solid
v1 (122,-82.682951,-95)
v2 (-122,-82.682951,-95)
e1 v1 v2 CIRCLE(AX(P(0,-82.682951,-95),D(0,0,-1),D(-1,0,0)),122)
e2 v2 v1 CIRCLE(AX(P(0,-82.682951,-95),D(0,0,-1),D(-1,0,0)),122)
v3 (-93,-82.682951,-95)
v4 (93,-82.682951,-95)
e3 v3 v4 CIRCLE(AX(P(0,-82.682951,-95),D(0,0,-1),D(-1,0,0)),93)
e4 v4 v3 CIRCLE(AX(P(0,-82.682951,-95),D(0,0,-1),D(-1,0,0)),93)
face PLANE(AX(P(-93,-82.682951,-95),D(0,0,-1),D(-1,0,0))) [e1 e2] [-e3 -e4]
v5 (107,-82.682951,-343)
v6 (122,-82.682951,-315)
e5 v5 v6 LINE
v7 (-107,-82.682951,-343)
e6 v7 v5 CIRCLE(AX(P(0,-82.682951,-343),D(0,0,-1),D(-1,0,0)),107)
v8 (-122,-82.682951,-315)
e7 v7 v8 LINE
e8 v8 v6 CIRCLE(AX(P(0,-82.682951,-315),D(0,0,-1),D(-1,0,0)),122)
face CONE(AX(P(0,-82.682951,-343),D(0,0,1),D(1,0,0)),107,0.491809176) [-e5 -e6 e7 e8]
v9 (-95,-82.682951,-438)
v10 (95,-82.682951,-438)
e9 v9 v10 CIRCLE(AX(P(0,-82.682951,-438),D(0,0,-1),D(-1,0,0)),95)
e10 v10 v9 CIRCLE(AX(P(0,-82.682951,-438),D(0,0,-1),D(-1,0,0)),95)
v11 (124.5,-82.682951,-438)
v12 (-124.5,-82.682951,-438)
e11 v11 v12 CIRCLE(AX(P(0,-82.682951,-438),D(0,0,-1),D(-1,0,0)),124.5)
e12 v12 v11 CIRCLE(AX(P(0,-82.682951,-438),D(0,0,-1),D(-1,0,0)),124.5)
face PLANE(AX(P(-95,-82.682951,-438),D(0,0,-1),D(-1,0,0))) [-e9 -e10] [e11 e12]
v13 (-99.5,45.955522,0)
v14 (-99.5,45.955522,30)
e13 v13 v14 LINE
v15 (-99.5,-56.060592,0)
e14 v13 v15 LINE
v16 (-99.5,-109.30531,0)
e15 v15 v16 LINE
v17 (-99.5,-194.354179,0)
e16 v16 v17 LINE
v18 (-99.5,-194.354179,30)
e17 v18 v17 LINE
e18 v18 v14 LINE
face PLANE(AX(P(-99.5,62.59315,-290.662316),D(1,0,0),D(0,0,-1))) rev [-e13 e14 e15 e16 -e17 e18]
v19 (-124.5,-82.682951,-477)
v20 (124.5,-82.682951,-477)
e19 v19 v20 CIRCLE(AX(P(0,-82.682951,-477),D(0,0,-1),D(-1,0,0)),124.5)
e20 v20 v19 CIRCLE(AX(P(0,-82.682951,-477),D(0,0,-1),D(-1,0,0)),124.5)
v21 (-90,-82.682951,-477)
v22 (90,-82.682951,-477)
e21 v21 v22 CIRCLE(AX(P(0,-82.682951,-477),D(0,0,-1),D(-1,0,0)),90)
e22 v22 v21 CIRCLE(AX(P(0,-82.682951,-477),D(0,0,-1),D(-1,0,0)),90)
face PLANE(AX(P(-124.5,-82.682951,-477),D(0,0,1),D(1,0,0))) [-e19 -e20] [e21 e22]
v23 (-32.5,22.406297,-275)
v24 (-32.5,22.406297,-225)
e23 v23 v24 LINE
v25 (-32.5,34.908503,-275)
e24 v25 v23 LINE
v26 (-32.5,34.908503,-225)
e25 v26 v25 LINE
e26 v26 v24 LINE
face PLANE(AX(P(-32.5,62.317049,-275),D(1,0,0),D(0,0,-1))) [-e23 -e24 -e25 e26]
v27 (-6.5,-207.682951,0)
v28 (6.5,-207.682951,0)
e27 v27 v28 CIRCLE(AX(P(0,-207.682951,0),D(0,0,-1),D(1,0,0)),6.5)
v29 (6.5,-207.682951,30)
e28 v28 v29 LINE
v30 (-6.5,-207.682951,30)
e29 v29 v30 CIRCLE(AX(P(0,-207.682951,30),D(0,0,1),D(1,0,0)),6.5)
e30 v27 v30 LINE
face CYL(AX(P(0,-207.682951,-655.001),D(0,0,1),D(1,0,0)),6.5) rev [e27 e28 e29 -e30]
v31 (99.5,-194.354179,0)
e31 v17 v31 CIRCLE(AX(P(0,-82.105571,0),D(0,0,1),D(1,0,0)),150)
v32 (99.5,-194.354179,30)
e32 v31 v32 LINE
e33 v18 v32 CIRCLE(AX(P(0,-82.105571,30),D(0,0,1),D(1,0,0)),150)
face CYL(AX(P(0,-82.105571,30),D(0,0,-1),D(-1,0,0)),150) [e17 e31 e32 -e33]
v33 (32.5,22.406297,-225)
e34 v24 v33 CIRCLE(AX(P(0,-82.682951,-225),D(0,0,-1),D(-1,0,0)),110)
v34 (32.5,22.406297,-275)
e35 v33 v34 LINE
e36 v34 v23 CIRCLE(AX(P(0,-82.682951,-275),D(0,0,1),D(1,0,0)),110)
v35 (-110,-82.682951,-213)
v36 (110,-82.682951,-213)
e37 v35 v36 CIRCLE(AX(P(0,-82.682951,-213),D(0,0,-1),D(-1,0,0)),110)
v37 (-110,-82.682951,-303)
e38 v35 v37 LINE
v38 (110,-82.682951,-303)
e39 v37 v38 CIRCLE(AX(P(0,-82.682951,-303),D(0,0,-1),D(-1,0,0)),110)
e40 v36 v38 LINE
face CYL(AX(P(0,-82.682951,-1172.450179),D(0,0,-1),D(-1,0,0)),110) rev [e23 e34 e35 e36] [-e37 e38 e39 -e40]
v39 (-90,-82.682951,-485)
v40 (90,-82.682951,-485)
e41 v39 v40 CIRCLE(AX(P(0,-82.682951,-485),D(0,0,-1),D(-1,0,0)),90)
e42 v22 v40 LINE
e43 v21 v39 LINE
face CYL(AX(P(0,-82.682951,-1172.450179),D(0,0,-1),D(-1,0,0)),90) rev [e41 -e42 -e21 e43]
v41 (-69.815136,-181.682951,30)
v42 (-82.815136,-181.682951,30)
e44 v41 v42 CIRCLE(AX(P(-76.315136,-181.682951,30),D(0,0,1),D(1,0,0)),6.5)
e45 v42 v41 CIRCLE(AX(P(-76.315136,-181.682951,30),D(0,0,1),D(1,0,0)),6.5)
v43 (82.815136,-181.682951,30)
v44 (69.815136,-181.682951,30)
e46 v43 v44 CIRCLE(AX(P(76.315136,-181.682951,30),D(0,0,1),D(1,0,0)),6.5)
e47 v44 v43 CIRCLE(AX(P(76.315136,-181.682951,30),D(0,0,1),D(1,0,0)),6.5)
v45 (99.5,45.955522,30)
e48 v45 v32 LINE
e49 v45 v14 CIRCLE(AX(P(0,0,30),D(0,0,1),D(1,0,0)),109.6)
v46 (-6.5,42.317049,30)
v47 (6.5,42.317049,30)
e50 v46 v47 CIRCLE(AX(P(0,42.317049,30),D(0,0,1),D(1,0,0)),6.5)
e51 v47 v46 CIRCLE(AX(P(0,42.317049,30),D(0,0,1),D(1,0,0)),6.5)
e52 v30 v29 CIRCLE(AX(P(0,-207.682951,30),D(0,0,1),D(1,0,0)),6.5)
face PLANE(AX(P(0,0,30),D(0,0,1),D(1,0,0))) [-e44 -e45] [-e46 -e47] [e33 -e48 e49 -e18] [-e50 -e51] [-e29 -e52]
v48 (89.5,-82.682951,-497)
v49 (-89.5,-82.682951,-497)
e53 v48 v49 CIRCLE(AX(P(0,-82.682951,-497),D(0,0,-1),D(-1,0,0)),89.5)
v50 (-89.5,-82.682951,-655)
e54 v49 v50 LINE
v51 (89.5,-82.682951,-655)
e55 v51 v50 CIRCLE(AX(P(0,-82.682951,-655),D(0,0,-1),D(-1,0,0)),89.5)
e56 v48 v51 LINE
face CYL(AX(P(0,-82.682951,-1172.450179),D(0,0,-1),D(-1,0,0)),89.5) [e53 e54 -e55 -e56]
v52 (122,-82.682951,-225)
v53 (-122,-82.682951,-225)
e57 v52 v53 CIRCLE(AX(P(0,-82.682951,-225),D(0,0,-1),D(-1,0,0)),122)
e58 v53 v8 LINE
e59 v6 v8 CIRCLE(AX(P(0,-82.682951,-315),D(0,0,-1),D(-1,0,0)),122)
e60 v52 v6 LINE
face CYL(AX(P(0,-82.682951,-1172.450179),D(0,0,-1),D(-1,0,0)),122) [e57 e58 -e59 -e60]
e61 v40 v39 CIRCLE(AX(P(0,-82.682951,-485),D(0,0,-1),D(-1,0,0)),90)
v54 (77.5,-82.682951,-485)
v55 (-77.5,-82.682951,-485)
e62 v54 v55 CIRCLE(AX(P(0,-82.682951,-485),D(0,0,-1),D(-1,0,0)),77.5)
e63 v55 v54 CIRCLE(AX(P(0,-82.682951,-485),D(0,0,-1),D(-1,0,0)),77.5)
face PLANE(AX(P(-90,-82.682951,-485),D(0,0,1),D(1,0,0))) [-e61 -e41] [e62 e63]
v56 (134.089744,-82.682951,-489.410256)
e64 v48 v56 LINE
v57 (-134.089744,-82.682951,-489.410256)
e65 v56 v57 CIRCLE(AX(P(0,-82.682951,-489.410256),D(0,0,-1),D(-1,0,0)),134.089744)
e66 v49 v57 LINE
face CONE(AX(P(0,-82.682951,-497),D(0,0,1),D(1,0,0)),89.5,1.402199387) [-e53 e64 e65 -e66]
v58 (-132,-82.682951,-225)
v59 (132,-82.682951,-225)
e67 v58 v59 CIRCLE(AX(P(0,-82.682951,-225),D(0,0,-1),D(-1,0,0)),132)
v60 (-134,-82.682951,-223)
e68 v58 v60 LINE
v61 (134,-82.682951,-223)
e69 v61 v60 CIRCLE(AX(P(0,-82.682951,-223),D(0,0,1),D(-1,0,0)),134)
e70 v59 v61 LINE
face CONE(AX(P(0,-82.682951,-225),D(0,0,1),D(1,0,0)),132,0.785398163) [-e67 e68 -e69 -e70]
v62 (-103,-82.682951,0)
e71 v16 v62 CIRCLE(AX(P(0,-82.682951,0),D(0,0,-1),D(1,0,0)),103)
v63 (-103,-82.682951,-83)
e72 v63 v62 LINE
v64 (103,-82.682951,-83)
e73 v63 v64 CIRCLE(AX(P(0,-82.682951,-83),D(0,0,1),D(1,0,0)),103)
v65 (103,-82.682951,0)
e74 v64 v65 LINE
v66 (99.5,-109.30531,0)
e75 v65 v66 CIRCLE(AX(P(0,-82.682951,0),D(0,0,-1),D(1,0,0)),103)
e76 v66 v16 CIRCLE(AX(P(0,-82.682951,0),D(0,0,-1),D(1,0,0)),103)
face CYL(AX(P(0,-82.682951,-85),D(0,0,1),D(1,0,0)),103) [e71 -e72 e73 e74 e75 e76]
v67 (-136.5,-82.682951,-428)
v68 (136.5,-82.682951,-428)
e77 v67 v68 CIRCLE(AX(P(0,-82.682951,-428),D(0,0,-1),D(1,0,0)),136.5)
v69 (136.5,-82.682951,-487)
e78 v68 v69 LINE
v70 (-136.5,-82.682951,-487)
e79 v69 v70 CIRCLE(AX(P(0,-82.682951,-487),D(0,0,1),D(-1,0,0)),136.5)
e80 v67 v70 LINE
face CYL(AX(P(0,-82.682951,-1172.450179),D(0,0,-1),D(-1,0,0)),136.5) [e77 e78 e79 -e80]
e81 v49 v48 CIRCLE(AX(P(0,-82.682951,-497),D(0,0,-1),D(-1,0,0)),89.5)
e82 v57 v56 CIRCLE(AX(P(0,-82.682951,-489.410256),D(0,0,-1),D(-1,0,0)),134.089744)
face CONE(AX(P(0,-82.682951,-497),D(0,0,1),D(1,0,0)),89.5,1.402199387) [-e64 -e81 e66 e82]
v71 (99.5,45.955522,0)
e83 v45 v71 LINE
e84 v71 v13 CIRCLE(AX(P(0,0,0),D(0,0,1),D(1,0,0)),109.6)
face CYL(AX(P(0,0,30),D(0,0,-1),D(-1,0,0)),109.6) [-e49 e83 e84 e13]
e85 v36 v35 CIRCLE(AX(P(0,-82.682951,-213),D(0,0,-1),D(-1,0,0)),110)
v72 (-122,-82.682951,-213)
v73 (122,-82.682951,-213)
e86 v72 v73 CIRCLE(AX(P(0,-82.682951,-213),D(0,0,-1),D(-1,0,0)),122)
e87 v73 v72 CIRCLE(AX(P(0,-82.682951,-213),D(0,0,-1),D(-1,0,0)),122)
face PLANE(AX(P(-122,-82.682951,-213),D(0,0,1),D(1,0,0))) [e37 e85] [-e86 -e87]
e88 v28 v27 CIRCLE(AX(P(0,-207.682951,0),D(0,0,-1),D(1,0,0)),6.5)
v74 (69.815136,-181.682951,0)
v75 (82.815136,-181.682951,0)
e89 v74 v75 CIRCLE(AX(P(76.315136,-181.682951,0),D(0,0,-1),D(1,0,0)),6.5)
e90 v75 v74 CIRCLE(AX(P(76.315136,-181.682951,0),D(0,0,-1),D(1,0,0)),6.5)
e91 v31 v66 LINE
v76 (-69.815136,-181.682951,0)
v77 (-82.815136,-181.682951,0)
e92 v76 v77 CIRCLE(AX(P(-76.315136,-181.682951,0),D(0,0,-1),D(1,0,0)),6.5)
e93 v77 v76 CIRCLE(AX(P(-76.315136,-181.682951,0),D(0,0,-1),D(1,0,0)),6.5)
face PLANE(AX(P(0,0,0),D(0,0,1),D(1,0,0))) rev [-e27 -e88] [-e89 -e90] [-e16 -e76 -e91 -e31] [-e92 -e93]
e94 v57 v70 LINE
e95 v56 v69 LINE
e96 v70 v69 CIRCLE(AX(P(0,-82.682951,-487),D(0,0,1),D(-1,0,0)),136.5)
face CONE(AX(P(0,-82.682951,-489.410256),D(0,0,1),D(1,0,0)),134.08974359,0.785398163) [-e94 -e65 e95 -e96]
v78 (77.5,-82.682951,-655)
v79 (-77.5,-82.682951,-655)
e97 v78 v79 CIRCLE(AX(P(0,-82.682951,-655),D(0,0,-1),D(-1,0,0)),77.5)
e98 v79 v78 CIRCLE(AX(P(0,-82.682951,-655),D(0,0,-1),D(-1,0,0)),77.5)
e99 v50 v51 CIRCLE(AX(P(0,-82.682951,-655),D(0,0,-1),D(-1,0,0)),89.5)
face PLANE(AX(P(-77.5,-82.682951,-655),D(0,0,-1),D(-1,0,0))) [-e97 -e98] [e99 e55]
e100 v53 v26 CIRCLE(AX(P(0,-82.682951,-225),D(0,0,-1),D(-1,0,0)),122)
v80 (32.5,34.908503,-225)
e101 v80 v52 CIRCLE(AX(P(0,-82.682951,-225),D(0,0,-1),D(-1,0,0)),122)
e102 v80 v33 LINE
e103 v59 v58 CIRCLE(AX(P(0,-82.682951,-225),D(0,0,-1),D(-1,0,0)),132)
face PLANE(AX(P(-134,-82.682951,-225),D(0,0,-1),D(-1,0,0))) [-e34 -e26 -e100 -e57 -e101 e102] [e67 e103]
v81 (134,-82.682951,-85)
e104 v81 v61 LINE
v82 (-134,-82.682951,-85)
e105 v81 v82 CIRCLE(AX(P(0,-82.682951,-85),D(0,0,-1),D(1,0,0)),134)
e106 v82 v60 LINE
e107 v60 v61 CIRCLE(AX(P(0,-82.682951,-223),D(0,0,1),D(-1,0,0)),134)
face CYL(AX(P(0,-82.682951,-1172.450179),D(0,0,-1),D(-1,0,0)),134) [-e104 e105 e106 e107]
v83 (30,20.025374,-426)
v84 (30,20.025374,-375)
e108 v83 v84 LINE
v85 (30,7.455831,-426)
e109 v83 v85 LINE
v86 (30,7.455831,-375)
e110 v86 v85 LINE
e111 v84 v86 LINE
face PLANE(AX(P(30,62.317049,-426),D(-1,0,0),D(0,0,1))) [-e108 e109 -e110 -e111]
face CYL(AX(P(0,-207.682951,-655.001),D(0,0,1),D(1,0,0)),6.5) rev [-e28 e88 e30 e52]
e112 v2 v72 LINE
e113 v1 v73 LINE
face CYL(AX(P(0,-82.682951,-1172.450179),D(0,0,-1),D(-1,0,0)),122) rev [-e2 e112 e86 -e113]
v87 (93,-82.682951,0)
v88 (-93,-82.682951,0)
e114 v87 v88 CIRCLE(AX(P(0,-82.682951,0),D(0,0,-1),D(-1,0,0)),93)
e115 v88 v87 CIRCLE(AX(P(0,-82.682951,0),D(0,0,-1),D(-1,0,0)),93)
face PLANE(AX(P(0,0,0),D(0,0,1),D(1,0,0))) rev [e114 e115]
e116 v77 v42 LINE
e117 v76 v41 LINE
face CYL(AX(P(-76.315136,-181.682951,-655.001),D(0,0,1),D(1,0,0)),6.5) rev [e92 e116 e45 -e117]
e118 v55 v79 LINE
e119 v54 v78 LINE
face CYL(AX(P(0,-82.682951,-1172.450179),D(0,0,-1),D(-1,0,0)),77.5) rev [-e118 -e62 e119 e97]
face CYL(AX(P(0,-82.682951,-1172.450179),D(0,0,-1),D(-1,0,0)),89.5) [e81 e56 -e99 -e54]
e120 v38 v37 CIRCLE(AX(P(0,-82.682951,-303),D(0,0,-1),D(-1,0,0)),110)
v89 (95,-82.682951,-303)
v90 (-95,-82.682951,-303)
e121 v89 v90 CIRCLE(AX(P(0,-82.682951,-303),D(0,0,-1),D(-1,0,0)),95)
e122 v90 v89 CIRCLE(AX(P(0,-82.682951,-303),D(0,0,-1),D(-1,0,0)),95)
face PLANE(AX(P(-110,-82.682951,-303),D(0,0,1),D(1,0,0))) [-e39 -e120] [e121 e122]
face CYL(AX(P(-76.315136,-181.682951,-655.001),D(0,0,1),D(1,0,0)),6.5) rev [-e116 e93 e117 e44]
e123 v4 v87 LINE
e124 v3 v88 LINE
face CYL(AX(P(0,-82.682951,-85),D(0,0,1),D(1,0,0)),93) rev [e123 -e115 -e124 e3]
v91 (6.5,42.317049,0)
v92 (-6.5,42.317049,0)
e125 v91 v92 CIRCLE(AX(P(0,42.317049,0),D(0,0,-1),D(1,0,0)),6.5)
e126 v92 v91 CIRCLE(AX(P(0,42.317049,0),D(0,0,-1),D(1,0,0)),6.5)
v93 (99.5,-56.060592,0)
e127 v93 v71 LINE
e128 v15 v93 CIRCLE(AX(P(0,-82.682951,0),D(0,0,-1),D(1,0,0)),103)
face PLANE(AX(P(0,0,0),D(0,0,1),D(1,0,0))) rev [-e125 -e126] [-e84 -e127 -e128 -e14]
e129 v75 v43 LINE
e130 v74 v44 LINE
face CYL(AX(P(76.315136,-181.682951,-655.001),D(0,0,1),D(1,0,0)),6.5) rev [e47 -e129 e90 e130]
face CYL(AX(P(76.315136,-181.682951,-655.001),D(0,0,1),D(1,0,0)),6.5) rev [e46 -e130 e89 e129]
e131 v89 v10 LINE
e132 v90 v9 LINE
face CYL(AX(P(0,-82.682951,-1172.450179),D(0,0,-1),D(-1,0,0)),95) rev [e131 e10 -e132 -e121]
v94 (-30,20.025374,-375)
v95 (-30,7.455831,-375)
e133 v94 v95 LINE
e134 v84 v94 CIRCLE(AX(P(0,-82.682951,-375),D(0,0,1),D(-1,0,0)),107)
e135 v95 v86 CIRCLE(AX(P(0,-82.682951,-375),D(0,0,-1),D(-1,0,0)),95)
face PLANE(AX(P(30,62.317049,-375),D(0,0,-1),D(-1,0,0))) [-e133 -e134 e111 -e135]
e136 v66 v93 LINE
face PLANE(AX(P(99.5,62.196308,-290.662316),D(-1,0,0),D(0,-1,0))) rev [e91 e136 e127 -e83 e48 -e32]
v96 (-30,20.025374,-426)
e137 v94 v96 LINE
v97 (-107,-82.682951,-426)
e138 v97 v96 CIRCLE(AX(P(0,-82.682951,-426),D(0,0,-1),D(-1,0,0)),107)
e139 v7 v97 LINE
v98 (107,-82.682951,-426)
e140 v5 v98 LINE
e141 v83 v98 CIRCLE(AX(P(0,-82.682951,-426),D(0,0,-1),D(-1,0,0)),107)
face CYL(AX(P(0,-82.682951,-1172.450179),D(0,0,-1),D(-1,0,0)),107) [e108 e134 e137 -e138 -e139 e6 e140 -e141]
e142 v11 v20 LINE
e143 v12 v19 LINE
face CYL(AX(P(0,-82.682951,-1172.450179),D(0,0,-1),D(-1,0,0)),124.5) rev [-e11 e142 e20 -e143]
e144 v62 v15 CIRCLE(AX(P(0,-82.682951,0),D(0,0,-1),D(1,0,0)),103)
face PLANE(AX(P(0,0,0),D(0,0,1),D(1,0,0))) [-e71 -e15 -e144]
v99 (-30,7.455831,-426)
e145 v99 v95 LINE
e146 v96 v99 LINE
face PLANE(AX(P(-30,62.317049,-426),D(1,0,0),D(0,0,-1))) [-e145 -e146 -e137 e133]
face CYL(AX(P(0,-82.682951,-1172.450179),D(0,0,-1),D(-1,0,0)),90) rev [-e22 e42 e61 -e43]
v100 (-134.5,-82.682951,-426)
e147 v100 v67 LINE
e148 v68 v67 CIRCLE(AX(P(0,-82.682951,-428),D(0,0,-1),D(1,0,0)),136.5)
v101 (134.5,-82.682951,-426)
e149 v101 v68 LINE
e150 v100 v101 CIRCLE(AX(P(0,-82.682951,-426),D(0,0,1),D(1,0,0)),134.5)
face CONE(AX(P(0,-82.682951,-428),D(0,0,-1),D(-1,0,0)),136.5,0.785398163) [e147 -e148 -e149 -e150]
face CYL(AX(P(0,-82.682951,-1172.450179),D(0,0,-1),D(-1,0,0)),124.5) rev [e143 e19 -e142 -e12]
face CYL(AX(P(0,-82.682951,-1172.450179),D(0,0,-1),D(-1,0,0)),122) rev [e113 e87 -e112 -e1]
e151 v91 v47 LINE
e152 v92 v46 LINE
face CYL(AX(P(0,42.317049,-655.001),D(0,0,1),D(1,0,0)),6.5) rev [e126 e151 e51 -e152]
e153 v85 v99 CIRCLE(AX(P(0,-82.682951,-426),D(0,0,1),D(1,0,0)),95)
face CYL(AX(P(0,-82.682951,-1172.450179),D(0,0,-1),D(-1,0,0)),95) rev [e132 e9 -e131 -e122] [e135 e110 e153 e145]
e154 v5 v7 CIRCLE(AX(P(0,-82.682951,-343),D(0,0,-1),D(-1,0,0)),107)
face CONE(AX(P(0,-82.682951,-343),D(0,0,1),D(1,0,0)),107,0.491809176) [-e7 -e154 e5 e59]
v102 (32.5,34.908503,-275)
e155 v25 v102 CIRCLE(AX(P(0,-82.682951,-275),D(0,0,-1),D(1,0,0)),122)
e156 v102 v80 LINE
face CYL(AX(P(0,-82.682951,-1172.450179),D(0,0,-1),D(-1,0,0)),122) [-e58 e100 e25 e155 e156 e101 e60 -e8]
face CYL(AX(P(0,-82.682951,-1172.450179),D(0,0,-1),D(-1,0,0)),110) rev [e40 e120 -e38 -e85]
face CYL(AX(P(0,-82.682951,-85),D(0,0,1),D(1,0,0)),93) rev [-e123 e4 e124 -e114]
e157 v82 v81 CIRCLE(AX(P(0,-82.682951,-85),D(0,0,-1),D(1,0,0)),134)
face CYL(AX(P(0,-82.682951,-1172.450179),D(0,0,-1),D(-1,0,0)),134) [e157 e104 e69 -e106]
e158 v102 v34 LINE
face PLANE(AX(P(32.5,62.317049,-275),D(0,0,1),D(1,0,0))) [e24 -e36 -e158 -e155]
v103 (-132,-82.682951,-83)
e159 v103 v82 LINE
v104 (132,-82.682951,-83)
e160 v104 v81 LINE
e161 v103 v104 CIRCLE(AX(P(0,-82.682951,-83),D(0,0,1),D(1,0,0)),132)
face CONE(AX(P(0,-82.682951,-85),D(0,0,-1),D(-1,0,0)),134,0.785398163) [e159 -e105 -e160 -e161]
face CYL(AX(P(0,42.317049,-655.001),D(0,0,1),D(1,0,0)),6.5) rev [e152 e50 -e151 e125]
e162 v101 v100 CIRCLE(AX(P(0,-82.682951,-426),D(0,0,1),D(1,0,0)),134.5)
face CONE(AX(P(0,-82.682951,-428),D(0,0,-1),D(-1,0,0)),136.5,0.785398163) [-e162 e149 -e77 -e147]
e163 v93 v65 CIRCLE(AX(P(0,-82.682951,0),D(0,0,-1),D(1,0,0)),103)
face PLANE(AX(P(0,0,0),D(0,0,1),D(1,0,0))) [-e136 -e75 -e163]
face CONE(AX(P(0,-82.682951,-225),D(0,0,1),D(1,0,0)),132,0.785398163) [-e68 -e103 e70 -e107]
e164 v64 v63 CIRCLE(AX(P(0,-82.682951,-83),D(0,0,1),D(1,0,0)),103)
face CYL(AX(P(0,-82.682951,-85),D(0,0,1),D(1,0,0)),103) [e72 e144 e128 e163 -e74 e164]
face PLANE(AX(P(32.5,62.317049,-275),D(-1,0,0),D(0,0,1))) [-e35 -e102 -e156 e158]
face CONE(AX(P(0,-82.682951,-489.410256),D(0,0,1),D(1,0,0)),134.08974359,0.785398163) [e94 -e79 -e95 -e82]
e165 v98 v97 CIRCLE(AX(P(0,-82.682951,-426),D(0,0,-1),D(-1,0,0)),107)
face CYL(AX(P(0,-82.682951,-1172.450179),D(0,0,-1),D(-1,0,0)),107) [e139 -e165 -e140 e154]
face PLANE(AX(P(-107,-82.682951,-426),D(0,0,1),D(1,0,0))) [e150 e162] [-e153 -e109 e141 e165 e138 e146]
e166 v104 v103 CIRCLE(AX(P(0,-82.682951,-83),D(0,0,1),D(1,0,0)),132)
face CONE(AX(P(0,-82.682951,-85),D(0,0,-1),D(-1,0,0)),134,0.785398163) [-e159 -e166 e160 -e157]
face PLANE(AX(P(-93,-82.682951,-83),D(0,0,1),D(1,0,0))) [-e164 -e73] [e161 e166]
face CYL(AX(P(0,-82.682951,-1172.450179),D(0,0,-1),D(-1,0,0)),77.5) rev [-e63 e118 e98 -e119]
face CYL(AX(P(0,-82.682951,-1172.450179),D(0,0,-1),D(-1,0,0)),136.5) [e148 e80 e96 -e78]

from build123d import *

# Parameters (mm, degrees)
EXTRUDE_1_DEPTH     = 30
SKETCH_3_R          = 103
SKETCH_3_R_2        = 93
EXTRUDE_2_DEPTH     = 85
CHAMFER_1_SIZE      = 2
CHAMFER_1_SIZE2     = 2.444922552
CHAMFER_2_SIZE      = 2
SKETCH_5_W          = 50
SKETCH_5_H          = 65
SKETCH_5_W_2        = 51
SKETCH_5_H_2        = 60
CUT_EXTRUDE_1_DEPTH = 145
CUT_EXTRUDE_2_REACH = 738.023
SKETCH_6_R          = 6.5
SKETCH_7_W          = 8
SKETCH_7_H          = 290.552201754
SKETCH_7_H_2        = 289.758517494
CUT_EXTRUDE_3_DEPTH = 30


with BuildPart() as part:
    # 草图2 → 凸台-拉伸1 (new body)
    with BuildSketch(Plane.XY):
        with BuildLine():
            Line((-107.5, 21.352049082), (-107.5, -186.717950918))
            ThreePointArc((-107.5, -186.717950918), (0, -232.105571153), (107.5, -186.717950918))
            Line((107.5, -186.717950918), (107.5, 21.352049082))
            ThreePointArc((107.5, 21.352049082), (0, 109.6), (-107.5, 21.352049082))
        make_face()
    extrude(amount=EXTRUDE_1_DEPTH)

    # 草图3 → 凸台-拉伸2 (add)
    with BuildSketch(Plane(origin=(0, 0, 0), x_dir=(-1, 0, 0), z_dir=(0, 0, -1))):
        with Locations(Location((0, -82.682950918, 0), (0, 0, 180))):
            Circle(SKETCH_3_R)
        with Locations((0, -82.682950918)):
            Circle(SKETCH_3_R_2, mode=Mode.SUBTRACT)
    extrude(amount=EXTRUDE_2_DEPTH)

    # 草图4 → 旋转1 (revolve)
    with BuildSketch(Plane.ZX.offset(-82.682950918)):
        Polygon((-95, -93), (-95, -122), (-213, -122), (-213, -110), (-303, -110), (-303, -95), (-438, -95), (-438, -124.5), (-477, -124.5), (-477, -90), (-485, -90), (-485, -77.5), (-655, -77.5), (-655, -89.5), (-497, -89.5), (-489, -136.5), (-426, -136.5), (-426, -107), (-343, -107), (-315, -122), (-225, -122), (-225, -134), (-83, -134), (-83, -93), align=None)
    revolve(axis=Axis((0, -82.682950918, -1172.450178842), (0, 0, 1)))

    # 倒角1
    chamfer_1_edges = [part.edges().sort_by_distance(p)[0] for p in [
        (136.5, -82.682950918, -489),
    ]]
    chamfer_1_side = [part.faces().sort_by_distance(p)[0] for p in [
        (136.5, -82.682950918, -457.5),
    ]]
    chamfer(chamfer_1_edges, length=CHAMFER_1_SIZE, length2=CHAMFER_1_SIZE2, reference=chamfer_1_side[0])

    # 倒角2
    chamfer_2_edges = [part.edges().sort_by_distance(p)[0] for p in [
        (134, -82.682950918, -83),
        (134, -82.682950918, -225),
        (136.5, -82.682950918, -426),
    ]]
    chamfer(chamfer_2_edges, length=CHAMFER_2_SIZE)

    # 草图5 → 切除-拉伸1 (cut)
    with BuildSketch(Plane.ZX.offset(-82.682950918)):
        with Locations((-250, 0)):
            Rectangle(SKETCH_5_W, SKETCH_5_H)
        with Locations((-400.5, 0)):
            Rectangle(SKETCH_5_W_2, SKETCH_5_H_2)
    extrude(amount=CUT_EXTRUDE_1_DEPTH, mode=Mode.SUBTRACT)

    # 草图6 → 切除-拉伸2 (cut, up to next)
    with BuildSketch(Plane.XY.offset(30), mode=Mode.PRIVATE) as cut_extrude_2_sk1:
        with Locations((0, 42.317049082)):
            Circle(SKETCH_6_R)
    cut_extrude_2_tool1 = extrude(cut_extrude_2_sk1.sketch, amount=-CUT_EXTRUDE_2_REACH, mode=Mode.PRIVATE) & part.part
    # 草图6 → 切除-拉伸2 (cut, up to next)
    with BuildSketch(Plane.XY.offset(30), mode=Mode.PRIVATE) as cut_extrude_2_sk2:
        with Locations((0, -207.682950918)):
            Circle(SKETCH_6_R)
    cut_extrude_2_tool2 = extrude(cut_extrude_2_sk2.sketch, amount=-CUT_EXTRUDE_2_REACH, mode=Mode.PRIVATE) & part.part
    # 草图6 → 切除-拉伸2 (cut, up to next)
    with BuildSketch(Plane.XY.offset(30), mode=Mode.PRIVATE) as cut_extrude_2_sk3:
        with Locations((-76.315136113, -181.682950918)):
            Circle(SKETCH_6_R)
    cut_extrude_2_tool3 = extrude(cut_extrude_2_sk3.sketch, amount=-CUT_EXTRUDE_2_REACH, mode=Mode.PRIVATE) & part.part
    # 草图6 → 切除-拉伸2 (cut, up to next)
    with BuildSketch(Plane.XY.offset(30), mode=Mode.PRIVATE) as cut_extrude_2_sk4:
        with Locations((76.315136113, -181.682950918)):
            Circle(SKETCH_6_R)
    cut_extrude_2_tool4 = extrude(cut_extrude_2_sk4.sketch, amount=-CUT_EXTRUDE_2_REACH, mode=Mode.PRIVATE) & part.part
    add(cut_extrude_2_tool1.solids().sort_by_distance((0, 42.317049, 30))[0], mode=Mode.SUBTRACT)
    add(cut_extrude_2_tool2.solids().sort_by_distance((0, -207.682951, 30))[0], mode=Mode.SUBTRACT)
    add(cut_extrude_2_tool3.solids().sort_by_distance((-76.315136, -181.682951, 30))[0], mode=Mode.SUBTRACT)
    add(cut_extrude_2_tool4.solids().sort_by_distance((76.315136, -181.682951, 30))[0], mode=Mode.SUBTRACT)

    # 草图7 → 切除-拉伸3 (cut)
    with BuildSketch(Plane.XY.offset(30)):
        with Locations((-103.5, -82.682950918)):
            Rectangle(SKETCH_7_W, SKETCH_7_H)
        with Locations((103.5, -82.682950918)):
            Rectangle(SKETCH_7_W, SKETCH_7_H_2)
    extrude(amount=-CUT_EXTRUDE_3_DEPTH, mode=Mode.SUBTRACT)


solid = part.part
